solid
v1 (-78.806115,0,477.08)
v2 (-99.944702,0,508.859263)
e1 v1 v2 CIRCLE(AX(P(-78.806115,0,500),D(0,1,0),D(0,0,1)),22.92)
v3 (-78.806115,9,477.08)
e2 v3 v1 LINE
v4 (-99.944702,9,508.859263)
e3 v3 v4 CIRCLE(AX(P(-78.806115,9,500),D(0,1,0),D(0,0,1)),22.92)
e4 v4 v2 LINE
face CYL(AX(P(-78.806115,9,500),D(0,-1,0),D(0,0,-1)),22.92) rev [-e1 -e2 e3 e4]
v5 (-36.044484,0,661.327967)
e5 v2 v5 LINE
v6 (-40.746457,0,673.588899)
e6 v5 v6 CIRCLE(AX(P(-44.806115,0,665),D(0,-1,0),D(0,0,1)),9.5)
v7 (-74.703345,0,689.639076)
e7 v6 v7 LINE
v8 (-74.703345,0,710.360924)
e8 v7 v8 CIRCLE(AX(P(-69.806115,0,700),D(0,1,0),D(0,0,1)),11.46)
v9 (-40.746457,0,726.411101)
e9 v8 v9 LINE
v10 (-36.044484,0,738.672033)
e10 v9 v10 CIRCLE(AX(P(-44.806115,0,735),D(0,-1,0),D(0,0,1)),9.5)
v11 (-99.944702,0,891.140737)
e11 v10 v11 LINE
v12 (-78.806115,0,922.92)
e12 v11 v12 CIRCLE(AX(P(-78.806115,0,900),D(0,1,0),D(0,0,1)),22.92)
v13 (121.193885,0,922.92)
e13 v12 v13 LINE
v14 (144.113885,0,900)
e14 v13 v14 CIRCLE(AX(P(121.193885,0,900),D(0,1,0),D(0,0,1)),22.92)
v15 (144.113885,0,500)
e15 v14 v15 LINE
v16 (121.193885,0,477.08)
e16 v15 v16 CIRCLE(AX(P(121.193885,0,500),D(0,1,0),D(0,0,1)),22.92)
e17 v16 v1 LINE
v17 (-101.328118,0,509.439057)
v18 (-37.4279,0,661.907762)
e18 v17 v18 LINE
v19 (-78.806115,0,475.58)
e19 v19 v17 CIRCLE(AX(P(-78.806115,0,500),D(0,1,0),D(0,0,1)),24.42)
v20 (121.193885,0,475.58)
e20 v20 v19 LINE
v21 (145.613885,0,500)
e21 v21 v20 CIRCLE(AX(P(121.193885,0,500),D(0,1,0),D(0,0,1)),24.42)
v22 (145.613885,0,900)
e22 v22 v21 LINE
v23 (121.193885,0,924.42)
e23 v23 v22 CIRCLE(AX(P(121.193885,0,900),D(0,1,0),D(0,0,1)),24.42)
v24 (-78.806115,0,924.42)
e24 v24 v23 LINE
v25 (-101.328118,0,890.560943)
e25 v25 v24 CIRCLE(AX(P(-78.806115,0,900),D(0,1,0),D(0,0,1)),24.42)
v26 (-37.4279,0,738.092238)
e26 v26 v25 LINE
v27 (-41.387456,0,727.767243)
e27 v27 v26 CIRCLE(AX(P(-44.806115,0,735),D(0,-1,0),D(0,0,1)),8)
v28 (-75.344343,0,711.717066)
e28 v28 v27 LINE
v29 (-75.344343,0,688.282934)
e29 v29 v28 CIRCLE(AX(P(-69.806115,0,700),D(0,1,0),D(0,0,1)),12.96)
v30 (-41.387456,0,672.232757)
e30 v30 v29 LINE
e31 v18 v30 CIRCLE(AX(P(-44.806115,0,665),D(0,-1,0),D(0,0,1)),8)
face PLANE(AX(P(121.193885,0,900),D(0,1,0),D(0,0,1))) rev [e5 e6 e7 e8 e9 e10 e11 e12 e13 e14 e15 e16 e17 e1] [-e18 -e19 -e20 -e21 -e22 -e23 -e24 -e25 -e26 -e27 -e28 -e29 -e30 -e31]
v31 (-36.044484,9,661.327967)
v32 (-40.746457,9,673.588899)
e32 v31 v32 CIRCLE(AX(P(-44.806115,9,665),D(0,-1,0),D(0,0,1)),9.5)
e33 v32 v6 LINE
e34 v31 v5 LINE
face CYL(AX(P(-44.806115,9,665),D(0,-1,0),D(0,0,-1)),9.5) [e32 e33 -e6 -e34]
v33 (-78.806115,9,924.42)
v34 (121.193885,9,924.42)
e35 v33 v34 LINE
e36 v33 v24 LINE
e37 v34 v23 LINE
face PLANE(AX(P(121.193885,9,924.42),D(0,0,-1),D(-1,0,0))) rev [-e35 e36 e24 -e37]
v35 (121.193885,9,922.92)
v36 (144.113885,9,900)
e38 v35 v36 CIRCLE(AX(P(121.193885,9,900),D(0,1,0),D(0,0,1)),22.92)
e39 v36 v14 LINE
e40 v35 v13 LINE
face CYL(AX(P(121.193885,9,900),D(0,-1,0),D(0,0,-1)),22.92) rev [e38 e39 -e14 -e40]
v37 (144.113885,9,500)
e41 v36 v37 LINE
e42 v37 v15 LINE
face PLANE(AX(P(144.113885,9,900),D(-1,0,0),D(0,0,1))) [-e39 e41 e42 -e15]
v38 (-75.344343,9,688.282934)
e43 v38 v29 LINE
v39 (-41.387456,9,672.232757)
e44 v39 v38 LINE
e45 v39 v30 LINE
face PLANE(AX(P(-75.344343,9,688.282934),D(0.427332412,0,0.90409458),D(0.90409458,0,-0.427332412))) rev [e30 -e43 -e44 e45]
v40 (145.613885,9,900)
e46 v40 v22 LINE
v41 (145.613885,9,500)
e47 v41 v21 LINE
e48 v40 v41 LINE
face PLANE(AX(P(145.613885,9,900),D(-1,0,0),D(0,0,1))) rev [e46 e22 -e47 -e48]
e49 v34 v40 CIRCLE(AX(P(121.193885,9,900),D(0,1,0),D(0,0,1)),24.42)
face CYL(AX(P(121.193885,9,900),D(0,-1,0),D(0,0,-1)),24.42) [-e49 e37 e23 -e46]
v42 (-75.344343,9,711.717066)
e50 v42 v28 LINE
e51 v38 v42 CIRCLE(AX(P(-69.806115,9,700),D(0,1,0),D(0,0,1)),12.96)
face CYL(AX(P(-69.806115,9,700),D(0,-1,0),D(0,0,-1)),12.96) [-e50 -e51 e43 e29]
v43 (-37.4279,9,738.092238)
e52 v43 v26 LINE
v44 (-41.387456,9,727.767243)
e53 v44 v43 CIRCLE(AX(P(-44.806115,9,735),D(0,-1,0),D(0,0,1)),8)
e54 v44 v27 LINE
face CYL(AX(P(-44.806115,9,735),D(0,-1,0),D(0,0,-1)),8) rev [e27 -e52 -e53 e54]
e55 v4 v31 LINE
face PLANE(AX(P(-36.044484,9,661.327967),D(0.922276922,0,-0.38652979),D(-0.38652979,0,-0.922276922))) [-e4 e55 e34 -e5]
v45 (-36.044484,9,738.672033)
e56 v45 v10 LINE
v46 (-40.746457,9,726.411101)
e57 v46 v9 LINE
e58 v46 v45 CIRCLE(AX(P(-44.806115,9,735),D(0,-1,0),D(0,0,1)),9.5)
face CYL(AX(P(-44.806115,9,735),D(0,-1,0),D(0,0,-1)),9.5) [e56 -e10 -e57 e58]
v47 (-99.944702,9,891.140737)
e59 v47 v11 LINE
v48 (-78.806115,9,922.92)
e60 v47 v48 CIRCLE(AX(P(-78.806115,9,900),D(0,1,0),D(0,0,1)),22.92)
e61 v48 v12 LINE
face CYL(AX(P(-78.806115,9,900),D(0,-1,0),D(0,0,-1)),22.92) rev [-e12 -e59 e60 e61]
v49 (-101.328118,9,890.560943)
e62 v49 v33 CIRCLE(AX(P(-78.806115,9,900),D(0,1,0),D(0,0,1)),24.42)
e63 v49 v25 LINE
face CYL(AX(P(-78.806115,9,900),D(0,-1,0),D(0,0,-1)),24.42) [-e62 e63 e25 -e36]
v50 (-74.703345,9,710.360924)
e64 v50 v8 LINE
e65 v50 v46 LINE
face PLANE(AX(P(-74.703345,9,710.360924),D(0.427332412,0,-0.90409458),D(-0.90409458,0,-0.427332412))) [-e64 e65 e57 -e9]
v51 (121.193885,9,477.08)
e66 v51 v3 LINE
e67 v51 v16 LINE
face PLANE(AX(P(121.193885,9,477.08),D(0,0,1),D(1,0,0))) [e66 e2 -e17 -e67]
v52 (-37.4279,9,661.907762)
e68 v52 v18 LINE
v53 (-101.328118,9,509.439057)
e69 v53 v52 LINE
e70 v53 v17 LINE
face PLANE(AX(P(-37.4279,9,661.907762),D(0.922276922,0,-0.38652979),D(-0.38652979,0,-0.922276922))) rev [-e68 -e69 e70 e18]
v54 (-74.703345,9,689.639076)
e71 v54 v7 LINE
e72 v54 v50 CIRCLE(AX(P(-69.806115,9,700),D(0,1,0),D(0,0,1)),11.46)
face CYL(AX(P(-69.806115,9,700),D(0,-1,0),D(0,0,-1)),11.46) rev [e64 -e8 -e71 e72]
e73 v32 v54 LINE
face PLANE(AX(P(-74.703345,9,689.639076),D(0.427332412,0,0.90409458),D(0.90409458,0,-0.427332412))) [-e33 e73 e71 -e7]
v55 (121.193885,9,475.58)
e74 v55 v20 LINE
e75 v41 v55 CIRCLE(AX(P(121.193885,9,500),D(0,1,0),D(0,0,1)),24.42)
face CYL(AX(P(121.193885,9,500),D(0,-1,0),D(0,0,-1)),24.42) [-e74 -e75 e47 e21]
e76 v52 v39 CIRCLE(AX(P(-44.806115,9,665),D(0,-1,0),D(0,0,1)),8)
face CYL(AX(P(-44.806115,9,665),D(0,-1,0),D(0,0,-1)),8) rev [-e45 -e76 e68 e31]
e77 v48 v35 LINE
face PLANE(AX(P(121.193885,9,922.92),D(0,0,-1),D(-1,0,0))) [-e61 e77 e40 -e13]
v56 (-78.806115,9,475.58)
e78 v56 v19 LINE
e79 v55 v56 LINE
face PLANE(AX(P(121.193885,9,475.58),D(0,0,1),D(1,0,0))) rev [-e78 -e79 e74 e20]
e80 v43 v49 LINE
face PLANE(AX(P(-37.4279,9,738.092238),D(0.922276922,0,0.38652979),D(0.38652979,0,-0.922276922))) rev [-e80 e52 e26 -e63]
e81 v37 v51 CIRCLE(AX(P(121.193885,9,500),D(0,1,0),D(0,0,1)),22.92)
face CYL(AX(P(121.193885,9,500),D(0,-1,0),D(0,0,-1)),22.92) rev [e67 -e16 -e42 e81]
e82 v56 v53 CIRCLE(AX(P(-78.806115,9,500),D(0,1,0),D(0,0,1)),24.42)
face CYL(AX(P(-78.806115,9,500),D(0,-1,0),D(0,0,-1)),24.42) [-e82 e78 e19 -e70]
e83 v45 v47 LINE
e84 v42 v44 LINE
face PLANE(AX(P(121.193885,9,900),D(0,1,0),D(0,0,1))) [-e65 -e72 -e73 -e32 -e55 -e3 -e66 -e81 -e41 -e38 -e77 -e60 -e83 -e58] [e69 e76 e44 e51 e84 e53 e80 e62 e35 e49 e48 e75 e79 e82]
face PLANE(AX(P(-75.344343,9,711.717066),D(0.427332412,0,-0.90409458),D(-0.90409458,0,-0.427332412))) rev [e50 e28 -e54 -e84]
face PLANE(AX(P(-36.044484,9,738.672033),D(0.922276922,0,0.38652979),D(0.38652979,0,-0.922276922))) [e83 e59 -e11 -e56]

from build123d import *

# Parameters (mm, degrees)
BOSS_EXTRUDE1_DEPTH = 9


with BuildPart() as part:
    # Sketch1 → Boss-Extrude1 (new body)
    with BuildSketch(Plane(origin=(0, 0, 0), x_dir=(-1, 0, 0), z_dir=(0, 1, 0))):
        with BuildLine():
            Line((-145.613884922, 900), (-145.613884922, 500))
            ThreePointArc((-145.613884922, 500), (-138.461432518, 482.732452403), (-121.193884922, 475.58))
            Line((-121.193884922, 475.58), (78.806115078, 475.58))
            ThreePointArc((78.806115078, 475.58), (99.138824975, 486.475307462), (101.328117521, 509.439057473))
            Line((101.328117521, 509.439057473), (37.4278997, 661.90776168))
            ThreePointArc((37.4278997, 661.90776168), (37.336543074, 667.86452336), (41.387455782, 672.23275664))
            Line((41.387455782, 672.23275664), (75.344343138, 688.282934243))
            ThreePointArc((75.344343138, 688.282934243), (82.766115078, 700), (75.344343138, 711.717065757))
            Line((75.344343138, 711.717065757), (41.387455782, 727.76724336))
            ThreePointArc((41.387455782, 727.76724336), (37.336543074, 732.13547664), (37.4278997, 738.09223832))
            Line((37.4278997, 738.09223832), (101.328117521, 890.560942527))
            ThreePointArc((101.328117521, 890.560942527), (99.138824975, 913.524692538), (78.806115078, 924.42))
            Line((78.806115078, 924.42), (-121.193884922, 924.42))
            ThreePointArc((-121.193884922, 924.42), (-138.461432518, 917.267547597), (-145.613884922, 900))
        make_face()
        with BuildLine():
            Line((-144.113884922, 900), (-144.113884922, 500))
            ThreePointArc((-144.113884922, 500), (-137.400772347, 483.793112575), (-121.193884922, 477.08))
            Line((-121.193884922, 477.08), (78.806115078, 477.08))
            ThreePointArc((78.806115078, 477.08), (97.889887021, 487.306062532), (99.944702137, 508.859262788))
            Line((99.944702137, 508.859262788), (36.044484316, 661.327966995))
            ThreePointArc((36.044484316, 661.327966995), (35.935998324, 668.40162149), (40.746457164, 673.58889851))
            Line((40.746457164, 673.58889851), (74.70334452, 689.639076113))
            ThreePointArc((74.70334452, 689.639076113), (81.266115078, 700), (74.70334452, 710.360923887))
            Line((74.70334452, 710.360923887), (40.746457164, 726.41110149))
            ThreePointArc((40.746457164, 726.41110149), (35.935998324, 731.59837851), (36.044484316, 738.672033005))
            Line((36.044484316, 738.672033005), (99.944702137, 891.140737212))
            ThreePointArc((99.944702137, 891.140737212), (97.889887021, 912.693937468), (78.806115078, 922.92))
            Line((78.806115078, 922.92), (-121.193884922, 922.92))
            ThreePointArc((-121.193884922, 922.92), (-137.400772347, 916.206887425), (-144.113884922, 900))
        make_face(mode=Mode.SUBTRACT)
    extrude(amount=BOSS_EXTRUDE1_DEPTH)


solid = part.part
